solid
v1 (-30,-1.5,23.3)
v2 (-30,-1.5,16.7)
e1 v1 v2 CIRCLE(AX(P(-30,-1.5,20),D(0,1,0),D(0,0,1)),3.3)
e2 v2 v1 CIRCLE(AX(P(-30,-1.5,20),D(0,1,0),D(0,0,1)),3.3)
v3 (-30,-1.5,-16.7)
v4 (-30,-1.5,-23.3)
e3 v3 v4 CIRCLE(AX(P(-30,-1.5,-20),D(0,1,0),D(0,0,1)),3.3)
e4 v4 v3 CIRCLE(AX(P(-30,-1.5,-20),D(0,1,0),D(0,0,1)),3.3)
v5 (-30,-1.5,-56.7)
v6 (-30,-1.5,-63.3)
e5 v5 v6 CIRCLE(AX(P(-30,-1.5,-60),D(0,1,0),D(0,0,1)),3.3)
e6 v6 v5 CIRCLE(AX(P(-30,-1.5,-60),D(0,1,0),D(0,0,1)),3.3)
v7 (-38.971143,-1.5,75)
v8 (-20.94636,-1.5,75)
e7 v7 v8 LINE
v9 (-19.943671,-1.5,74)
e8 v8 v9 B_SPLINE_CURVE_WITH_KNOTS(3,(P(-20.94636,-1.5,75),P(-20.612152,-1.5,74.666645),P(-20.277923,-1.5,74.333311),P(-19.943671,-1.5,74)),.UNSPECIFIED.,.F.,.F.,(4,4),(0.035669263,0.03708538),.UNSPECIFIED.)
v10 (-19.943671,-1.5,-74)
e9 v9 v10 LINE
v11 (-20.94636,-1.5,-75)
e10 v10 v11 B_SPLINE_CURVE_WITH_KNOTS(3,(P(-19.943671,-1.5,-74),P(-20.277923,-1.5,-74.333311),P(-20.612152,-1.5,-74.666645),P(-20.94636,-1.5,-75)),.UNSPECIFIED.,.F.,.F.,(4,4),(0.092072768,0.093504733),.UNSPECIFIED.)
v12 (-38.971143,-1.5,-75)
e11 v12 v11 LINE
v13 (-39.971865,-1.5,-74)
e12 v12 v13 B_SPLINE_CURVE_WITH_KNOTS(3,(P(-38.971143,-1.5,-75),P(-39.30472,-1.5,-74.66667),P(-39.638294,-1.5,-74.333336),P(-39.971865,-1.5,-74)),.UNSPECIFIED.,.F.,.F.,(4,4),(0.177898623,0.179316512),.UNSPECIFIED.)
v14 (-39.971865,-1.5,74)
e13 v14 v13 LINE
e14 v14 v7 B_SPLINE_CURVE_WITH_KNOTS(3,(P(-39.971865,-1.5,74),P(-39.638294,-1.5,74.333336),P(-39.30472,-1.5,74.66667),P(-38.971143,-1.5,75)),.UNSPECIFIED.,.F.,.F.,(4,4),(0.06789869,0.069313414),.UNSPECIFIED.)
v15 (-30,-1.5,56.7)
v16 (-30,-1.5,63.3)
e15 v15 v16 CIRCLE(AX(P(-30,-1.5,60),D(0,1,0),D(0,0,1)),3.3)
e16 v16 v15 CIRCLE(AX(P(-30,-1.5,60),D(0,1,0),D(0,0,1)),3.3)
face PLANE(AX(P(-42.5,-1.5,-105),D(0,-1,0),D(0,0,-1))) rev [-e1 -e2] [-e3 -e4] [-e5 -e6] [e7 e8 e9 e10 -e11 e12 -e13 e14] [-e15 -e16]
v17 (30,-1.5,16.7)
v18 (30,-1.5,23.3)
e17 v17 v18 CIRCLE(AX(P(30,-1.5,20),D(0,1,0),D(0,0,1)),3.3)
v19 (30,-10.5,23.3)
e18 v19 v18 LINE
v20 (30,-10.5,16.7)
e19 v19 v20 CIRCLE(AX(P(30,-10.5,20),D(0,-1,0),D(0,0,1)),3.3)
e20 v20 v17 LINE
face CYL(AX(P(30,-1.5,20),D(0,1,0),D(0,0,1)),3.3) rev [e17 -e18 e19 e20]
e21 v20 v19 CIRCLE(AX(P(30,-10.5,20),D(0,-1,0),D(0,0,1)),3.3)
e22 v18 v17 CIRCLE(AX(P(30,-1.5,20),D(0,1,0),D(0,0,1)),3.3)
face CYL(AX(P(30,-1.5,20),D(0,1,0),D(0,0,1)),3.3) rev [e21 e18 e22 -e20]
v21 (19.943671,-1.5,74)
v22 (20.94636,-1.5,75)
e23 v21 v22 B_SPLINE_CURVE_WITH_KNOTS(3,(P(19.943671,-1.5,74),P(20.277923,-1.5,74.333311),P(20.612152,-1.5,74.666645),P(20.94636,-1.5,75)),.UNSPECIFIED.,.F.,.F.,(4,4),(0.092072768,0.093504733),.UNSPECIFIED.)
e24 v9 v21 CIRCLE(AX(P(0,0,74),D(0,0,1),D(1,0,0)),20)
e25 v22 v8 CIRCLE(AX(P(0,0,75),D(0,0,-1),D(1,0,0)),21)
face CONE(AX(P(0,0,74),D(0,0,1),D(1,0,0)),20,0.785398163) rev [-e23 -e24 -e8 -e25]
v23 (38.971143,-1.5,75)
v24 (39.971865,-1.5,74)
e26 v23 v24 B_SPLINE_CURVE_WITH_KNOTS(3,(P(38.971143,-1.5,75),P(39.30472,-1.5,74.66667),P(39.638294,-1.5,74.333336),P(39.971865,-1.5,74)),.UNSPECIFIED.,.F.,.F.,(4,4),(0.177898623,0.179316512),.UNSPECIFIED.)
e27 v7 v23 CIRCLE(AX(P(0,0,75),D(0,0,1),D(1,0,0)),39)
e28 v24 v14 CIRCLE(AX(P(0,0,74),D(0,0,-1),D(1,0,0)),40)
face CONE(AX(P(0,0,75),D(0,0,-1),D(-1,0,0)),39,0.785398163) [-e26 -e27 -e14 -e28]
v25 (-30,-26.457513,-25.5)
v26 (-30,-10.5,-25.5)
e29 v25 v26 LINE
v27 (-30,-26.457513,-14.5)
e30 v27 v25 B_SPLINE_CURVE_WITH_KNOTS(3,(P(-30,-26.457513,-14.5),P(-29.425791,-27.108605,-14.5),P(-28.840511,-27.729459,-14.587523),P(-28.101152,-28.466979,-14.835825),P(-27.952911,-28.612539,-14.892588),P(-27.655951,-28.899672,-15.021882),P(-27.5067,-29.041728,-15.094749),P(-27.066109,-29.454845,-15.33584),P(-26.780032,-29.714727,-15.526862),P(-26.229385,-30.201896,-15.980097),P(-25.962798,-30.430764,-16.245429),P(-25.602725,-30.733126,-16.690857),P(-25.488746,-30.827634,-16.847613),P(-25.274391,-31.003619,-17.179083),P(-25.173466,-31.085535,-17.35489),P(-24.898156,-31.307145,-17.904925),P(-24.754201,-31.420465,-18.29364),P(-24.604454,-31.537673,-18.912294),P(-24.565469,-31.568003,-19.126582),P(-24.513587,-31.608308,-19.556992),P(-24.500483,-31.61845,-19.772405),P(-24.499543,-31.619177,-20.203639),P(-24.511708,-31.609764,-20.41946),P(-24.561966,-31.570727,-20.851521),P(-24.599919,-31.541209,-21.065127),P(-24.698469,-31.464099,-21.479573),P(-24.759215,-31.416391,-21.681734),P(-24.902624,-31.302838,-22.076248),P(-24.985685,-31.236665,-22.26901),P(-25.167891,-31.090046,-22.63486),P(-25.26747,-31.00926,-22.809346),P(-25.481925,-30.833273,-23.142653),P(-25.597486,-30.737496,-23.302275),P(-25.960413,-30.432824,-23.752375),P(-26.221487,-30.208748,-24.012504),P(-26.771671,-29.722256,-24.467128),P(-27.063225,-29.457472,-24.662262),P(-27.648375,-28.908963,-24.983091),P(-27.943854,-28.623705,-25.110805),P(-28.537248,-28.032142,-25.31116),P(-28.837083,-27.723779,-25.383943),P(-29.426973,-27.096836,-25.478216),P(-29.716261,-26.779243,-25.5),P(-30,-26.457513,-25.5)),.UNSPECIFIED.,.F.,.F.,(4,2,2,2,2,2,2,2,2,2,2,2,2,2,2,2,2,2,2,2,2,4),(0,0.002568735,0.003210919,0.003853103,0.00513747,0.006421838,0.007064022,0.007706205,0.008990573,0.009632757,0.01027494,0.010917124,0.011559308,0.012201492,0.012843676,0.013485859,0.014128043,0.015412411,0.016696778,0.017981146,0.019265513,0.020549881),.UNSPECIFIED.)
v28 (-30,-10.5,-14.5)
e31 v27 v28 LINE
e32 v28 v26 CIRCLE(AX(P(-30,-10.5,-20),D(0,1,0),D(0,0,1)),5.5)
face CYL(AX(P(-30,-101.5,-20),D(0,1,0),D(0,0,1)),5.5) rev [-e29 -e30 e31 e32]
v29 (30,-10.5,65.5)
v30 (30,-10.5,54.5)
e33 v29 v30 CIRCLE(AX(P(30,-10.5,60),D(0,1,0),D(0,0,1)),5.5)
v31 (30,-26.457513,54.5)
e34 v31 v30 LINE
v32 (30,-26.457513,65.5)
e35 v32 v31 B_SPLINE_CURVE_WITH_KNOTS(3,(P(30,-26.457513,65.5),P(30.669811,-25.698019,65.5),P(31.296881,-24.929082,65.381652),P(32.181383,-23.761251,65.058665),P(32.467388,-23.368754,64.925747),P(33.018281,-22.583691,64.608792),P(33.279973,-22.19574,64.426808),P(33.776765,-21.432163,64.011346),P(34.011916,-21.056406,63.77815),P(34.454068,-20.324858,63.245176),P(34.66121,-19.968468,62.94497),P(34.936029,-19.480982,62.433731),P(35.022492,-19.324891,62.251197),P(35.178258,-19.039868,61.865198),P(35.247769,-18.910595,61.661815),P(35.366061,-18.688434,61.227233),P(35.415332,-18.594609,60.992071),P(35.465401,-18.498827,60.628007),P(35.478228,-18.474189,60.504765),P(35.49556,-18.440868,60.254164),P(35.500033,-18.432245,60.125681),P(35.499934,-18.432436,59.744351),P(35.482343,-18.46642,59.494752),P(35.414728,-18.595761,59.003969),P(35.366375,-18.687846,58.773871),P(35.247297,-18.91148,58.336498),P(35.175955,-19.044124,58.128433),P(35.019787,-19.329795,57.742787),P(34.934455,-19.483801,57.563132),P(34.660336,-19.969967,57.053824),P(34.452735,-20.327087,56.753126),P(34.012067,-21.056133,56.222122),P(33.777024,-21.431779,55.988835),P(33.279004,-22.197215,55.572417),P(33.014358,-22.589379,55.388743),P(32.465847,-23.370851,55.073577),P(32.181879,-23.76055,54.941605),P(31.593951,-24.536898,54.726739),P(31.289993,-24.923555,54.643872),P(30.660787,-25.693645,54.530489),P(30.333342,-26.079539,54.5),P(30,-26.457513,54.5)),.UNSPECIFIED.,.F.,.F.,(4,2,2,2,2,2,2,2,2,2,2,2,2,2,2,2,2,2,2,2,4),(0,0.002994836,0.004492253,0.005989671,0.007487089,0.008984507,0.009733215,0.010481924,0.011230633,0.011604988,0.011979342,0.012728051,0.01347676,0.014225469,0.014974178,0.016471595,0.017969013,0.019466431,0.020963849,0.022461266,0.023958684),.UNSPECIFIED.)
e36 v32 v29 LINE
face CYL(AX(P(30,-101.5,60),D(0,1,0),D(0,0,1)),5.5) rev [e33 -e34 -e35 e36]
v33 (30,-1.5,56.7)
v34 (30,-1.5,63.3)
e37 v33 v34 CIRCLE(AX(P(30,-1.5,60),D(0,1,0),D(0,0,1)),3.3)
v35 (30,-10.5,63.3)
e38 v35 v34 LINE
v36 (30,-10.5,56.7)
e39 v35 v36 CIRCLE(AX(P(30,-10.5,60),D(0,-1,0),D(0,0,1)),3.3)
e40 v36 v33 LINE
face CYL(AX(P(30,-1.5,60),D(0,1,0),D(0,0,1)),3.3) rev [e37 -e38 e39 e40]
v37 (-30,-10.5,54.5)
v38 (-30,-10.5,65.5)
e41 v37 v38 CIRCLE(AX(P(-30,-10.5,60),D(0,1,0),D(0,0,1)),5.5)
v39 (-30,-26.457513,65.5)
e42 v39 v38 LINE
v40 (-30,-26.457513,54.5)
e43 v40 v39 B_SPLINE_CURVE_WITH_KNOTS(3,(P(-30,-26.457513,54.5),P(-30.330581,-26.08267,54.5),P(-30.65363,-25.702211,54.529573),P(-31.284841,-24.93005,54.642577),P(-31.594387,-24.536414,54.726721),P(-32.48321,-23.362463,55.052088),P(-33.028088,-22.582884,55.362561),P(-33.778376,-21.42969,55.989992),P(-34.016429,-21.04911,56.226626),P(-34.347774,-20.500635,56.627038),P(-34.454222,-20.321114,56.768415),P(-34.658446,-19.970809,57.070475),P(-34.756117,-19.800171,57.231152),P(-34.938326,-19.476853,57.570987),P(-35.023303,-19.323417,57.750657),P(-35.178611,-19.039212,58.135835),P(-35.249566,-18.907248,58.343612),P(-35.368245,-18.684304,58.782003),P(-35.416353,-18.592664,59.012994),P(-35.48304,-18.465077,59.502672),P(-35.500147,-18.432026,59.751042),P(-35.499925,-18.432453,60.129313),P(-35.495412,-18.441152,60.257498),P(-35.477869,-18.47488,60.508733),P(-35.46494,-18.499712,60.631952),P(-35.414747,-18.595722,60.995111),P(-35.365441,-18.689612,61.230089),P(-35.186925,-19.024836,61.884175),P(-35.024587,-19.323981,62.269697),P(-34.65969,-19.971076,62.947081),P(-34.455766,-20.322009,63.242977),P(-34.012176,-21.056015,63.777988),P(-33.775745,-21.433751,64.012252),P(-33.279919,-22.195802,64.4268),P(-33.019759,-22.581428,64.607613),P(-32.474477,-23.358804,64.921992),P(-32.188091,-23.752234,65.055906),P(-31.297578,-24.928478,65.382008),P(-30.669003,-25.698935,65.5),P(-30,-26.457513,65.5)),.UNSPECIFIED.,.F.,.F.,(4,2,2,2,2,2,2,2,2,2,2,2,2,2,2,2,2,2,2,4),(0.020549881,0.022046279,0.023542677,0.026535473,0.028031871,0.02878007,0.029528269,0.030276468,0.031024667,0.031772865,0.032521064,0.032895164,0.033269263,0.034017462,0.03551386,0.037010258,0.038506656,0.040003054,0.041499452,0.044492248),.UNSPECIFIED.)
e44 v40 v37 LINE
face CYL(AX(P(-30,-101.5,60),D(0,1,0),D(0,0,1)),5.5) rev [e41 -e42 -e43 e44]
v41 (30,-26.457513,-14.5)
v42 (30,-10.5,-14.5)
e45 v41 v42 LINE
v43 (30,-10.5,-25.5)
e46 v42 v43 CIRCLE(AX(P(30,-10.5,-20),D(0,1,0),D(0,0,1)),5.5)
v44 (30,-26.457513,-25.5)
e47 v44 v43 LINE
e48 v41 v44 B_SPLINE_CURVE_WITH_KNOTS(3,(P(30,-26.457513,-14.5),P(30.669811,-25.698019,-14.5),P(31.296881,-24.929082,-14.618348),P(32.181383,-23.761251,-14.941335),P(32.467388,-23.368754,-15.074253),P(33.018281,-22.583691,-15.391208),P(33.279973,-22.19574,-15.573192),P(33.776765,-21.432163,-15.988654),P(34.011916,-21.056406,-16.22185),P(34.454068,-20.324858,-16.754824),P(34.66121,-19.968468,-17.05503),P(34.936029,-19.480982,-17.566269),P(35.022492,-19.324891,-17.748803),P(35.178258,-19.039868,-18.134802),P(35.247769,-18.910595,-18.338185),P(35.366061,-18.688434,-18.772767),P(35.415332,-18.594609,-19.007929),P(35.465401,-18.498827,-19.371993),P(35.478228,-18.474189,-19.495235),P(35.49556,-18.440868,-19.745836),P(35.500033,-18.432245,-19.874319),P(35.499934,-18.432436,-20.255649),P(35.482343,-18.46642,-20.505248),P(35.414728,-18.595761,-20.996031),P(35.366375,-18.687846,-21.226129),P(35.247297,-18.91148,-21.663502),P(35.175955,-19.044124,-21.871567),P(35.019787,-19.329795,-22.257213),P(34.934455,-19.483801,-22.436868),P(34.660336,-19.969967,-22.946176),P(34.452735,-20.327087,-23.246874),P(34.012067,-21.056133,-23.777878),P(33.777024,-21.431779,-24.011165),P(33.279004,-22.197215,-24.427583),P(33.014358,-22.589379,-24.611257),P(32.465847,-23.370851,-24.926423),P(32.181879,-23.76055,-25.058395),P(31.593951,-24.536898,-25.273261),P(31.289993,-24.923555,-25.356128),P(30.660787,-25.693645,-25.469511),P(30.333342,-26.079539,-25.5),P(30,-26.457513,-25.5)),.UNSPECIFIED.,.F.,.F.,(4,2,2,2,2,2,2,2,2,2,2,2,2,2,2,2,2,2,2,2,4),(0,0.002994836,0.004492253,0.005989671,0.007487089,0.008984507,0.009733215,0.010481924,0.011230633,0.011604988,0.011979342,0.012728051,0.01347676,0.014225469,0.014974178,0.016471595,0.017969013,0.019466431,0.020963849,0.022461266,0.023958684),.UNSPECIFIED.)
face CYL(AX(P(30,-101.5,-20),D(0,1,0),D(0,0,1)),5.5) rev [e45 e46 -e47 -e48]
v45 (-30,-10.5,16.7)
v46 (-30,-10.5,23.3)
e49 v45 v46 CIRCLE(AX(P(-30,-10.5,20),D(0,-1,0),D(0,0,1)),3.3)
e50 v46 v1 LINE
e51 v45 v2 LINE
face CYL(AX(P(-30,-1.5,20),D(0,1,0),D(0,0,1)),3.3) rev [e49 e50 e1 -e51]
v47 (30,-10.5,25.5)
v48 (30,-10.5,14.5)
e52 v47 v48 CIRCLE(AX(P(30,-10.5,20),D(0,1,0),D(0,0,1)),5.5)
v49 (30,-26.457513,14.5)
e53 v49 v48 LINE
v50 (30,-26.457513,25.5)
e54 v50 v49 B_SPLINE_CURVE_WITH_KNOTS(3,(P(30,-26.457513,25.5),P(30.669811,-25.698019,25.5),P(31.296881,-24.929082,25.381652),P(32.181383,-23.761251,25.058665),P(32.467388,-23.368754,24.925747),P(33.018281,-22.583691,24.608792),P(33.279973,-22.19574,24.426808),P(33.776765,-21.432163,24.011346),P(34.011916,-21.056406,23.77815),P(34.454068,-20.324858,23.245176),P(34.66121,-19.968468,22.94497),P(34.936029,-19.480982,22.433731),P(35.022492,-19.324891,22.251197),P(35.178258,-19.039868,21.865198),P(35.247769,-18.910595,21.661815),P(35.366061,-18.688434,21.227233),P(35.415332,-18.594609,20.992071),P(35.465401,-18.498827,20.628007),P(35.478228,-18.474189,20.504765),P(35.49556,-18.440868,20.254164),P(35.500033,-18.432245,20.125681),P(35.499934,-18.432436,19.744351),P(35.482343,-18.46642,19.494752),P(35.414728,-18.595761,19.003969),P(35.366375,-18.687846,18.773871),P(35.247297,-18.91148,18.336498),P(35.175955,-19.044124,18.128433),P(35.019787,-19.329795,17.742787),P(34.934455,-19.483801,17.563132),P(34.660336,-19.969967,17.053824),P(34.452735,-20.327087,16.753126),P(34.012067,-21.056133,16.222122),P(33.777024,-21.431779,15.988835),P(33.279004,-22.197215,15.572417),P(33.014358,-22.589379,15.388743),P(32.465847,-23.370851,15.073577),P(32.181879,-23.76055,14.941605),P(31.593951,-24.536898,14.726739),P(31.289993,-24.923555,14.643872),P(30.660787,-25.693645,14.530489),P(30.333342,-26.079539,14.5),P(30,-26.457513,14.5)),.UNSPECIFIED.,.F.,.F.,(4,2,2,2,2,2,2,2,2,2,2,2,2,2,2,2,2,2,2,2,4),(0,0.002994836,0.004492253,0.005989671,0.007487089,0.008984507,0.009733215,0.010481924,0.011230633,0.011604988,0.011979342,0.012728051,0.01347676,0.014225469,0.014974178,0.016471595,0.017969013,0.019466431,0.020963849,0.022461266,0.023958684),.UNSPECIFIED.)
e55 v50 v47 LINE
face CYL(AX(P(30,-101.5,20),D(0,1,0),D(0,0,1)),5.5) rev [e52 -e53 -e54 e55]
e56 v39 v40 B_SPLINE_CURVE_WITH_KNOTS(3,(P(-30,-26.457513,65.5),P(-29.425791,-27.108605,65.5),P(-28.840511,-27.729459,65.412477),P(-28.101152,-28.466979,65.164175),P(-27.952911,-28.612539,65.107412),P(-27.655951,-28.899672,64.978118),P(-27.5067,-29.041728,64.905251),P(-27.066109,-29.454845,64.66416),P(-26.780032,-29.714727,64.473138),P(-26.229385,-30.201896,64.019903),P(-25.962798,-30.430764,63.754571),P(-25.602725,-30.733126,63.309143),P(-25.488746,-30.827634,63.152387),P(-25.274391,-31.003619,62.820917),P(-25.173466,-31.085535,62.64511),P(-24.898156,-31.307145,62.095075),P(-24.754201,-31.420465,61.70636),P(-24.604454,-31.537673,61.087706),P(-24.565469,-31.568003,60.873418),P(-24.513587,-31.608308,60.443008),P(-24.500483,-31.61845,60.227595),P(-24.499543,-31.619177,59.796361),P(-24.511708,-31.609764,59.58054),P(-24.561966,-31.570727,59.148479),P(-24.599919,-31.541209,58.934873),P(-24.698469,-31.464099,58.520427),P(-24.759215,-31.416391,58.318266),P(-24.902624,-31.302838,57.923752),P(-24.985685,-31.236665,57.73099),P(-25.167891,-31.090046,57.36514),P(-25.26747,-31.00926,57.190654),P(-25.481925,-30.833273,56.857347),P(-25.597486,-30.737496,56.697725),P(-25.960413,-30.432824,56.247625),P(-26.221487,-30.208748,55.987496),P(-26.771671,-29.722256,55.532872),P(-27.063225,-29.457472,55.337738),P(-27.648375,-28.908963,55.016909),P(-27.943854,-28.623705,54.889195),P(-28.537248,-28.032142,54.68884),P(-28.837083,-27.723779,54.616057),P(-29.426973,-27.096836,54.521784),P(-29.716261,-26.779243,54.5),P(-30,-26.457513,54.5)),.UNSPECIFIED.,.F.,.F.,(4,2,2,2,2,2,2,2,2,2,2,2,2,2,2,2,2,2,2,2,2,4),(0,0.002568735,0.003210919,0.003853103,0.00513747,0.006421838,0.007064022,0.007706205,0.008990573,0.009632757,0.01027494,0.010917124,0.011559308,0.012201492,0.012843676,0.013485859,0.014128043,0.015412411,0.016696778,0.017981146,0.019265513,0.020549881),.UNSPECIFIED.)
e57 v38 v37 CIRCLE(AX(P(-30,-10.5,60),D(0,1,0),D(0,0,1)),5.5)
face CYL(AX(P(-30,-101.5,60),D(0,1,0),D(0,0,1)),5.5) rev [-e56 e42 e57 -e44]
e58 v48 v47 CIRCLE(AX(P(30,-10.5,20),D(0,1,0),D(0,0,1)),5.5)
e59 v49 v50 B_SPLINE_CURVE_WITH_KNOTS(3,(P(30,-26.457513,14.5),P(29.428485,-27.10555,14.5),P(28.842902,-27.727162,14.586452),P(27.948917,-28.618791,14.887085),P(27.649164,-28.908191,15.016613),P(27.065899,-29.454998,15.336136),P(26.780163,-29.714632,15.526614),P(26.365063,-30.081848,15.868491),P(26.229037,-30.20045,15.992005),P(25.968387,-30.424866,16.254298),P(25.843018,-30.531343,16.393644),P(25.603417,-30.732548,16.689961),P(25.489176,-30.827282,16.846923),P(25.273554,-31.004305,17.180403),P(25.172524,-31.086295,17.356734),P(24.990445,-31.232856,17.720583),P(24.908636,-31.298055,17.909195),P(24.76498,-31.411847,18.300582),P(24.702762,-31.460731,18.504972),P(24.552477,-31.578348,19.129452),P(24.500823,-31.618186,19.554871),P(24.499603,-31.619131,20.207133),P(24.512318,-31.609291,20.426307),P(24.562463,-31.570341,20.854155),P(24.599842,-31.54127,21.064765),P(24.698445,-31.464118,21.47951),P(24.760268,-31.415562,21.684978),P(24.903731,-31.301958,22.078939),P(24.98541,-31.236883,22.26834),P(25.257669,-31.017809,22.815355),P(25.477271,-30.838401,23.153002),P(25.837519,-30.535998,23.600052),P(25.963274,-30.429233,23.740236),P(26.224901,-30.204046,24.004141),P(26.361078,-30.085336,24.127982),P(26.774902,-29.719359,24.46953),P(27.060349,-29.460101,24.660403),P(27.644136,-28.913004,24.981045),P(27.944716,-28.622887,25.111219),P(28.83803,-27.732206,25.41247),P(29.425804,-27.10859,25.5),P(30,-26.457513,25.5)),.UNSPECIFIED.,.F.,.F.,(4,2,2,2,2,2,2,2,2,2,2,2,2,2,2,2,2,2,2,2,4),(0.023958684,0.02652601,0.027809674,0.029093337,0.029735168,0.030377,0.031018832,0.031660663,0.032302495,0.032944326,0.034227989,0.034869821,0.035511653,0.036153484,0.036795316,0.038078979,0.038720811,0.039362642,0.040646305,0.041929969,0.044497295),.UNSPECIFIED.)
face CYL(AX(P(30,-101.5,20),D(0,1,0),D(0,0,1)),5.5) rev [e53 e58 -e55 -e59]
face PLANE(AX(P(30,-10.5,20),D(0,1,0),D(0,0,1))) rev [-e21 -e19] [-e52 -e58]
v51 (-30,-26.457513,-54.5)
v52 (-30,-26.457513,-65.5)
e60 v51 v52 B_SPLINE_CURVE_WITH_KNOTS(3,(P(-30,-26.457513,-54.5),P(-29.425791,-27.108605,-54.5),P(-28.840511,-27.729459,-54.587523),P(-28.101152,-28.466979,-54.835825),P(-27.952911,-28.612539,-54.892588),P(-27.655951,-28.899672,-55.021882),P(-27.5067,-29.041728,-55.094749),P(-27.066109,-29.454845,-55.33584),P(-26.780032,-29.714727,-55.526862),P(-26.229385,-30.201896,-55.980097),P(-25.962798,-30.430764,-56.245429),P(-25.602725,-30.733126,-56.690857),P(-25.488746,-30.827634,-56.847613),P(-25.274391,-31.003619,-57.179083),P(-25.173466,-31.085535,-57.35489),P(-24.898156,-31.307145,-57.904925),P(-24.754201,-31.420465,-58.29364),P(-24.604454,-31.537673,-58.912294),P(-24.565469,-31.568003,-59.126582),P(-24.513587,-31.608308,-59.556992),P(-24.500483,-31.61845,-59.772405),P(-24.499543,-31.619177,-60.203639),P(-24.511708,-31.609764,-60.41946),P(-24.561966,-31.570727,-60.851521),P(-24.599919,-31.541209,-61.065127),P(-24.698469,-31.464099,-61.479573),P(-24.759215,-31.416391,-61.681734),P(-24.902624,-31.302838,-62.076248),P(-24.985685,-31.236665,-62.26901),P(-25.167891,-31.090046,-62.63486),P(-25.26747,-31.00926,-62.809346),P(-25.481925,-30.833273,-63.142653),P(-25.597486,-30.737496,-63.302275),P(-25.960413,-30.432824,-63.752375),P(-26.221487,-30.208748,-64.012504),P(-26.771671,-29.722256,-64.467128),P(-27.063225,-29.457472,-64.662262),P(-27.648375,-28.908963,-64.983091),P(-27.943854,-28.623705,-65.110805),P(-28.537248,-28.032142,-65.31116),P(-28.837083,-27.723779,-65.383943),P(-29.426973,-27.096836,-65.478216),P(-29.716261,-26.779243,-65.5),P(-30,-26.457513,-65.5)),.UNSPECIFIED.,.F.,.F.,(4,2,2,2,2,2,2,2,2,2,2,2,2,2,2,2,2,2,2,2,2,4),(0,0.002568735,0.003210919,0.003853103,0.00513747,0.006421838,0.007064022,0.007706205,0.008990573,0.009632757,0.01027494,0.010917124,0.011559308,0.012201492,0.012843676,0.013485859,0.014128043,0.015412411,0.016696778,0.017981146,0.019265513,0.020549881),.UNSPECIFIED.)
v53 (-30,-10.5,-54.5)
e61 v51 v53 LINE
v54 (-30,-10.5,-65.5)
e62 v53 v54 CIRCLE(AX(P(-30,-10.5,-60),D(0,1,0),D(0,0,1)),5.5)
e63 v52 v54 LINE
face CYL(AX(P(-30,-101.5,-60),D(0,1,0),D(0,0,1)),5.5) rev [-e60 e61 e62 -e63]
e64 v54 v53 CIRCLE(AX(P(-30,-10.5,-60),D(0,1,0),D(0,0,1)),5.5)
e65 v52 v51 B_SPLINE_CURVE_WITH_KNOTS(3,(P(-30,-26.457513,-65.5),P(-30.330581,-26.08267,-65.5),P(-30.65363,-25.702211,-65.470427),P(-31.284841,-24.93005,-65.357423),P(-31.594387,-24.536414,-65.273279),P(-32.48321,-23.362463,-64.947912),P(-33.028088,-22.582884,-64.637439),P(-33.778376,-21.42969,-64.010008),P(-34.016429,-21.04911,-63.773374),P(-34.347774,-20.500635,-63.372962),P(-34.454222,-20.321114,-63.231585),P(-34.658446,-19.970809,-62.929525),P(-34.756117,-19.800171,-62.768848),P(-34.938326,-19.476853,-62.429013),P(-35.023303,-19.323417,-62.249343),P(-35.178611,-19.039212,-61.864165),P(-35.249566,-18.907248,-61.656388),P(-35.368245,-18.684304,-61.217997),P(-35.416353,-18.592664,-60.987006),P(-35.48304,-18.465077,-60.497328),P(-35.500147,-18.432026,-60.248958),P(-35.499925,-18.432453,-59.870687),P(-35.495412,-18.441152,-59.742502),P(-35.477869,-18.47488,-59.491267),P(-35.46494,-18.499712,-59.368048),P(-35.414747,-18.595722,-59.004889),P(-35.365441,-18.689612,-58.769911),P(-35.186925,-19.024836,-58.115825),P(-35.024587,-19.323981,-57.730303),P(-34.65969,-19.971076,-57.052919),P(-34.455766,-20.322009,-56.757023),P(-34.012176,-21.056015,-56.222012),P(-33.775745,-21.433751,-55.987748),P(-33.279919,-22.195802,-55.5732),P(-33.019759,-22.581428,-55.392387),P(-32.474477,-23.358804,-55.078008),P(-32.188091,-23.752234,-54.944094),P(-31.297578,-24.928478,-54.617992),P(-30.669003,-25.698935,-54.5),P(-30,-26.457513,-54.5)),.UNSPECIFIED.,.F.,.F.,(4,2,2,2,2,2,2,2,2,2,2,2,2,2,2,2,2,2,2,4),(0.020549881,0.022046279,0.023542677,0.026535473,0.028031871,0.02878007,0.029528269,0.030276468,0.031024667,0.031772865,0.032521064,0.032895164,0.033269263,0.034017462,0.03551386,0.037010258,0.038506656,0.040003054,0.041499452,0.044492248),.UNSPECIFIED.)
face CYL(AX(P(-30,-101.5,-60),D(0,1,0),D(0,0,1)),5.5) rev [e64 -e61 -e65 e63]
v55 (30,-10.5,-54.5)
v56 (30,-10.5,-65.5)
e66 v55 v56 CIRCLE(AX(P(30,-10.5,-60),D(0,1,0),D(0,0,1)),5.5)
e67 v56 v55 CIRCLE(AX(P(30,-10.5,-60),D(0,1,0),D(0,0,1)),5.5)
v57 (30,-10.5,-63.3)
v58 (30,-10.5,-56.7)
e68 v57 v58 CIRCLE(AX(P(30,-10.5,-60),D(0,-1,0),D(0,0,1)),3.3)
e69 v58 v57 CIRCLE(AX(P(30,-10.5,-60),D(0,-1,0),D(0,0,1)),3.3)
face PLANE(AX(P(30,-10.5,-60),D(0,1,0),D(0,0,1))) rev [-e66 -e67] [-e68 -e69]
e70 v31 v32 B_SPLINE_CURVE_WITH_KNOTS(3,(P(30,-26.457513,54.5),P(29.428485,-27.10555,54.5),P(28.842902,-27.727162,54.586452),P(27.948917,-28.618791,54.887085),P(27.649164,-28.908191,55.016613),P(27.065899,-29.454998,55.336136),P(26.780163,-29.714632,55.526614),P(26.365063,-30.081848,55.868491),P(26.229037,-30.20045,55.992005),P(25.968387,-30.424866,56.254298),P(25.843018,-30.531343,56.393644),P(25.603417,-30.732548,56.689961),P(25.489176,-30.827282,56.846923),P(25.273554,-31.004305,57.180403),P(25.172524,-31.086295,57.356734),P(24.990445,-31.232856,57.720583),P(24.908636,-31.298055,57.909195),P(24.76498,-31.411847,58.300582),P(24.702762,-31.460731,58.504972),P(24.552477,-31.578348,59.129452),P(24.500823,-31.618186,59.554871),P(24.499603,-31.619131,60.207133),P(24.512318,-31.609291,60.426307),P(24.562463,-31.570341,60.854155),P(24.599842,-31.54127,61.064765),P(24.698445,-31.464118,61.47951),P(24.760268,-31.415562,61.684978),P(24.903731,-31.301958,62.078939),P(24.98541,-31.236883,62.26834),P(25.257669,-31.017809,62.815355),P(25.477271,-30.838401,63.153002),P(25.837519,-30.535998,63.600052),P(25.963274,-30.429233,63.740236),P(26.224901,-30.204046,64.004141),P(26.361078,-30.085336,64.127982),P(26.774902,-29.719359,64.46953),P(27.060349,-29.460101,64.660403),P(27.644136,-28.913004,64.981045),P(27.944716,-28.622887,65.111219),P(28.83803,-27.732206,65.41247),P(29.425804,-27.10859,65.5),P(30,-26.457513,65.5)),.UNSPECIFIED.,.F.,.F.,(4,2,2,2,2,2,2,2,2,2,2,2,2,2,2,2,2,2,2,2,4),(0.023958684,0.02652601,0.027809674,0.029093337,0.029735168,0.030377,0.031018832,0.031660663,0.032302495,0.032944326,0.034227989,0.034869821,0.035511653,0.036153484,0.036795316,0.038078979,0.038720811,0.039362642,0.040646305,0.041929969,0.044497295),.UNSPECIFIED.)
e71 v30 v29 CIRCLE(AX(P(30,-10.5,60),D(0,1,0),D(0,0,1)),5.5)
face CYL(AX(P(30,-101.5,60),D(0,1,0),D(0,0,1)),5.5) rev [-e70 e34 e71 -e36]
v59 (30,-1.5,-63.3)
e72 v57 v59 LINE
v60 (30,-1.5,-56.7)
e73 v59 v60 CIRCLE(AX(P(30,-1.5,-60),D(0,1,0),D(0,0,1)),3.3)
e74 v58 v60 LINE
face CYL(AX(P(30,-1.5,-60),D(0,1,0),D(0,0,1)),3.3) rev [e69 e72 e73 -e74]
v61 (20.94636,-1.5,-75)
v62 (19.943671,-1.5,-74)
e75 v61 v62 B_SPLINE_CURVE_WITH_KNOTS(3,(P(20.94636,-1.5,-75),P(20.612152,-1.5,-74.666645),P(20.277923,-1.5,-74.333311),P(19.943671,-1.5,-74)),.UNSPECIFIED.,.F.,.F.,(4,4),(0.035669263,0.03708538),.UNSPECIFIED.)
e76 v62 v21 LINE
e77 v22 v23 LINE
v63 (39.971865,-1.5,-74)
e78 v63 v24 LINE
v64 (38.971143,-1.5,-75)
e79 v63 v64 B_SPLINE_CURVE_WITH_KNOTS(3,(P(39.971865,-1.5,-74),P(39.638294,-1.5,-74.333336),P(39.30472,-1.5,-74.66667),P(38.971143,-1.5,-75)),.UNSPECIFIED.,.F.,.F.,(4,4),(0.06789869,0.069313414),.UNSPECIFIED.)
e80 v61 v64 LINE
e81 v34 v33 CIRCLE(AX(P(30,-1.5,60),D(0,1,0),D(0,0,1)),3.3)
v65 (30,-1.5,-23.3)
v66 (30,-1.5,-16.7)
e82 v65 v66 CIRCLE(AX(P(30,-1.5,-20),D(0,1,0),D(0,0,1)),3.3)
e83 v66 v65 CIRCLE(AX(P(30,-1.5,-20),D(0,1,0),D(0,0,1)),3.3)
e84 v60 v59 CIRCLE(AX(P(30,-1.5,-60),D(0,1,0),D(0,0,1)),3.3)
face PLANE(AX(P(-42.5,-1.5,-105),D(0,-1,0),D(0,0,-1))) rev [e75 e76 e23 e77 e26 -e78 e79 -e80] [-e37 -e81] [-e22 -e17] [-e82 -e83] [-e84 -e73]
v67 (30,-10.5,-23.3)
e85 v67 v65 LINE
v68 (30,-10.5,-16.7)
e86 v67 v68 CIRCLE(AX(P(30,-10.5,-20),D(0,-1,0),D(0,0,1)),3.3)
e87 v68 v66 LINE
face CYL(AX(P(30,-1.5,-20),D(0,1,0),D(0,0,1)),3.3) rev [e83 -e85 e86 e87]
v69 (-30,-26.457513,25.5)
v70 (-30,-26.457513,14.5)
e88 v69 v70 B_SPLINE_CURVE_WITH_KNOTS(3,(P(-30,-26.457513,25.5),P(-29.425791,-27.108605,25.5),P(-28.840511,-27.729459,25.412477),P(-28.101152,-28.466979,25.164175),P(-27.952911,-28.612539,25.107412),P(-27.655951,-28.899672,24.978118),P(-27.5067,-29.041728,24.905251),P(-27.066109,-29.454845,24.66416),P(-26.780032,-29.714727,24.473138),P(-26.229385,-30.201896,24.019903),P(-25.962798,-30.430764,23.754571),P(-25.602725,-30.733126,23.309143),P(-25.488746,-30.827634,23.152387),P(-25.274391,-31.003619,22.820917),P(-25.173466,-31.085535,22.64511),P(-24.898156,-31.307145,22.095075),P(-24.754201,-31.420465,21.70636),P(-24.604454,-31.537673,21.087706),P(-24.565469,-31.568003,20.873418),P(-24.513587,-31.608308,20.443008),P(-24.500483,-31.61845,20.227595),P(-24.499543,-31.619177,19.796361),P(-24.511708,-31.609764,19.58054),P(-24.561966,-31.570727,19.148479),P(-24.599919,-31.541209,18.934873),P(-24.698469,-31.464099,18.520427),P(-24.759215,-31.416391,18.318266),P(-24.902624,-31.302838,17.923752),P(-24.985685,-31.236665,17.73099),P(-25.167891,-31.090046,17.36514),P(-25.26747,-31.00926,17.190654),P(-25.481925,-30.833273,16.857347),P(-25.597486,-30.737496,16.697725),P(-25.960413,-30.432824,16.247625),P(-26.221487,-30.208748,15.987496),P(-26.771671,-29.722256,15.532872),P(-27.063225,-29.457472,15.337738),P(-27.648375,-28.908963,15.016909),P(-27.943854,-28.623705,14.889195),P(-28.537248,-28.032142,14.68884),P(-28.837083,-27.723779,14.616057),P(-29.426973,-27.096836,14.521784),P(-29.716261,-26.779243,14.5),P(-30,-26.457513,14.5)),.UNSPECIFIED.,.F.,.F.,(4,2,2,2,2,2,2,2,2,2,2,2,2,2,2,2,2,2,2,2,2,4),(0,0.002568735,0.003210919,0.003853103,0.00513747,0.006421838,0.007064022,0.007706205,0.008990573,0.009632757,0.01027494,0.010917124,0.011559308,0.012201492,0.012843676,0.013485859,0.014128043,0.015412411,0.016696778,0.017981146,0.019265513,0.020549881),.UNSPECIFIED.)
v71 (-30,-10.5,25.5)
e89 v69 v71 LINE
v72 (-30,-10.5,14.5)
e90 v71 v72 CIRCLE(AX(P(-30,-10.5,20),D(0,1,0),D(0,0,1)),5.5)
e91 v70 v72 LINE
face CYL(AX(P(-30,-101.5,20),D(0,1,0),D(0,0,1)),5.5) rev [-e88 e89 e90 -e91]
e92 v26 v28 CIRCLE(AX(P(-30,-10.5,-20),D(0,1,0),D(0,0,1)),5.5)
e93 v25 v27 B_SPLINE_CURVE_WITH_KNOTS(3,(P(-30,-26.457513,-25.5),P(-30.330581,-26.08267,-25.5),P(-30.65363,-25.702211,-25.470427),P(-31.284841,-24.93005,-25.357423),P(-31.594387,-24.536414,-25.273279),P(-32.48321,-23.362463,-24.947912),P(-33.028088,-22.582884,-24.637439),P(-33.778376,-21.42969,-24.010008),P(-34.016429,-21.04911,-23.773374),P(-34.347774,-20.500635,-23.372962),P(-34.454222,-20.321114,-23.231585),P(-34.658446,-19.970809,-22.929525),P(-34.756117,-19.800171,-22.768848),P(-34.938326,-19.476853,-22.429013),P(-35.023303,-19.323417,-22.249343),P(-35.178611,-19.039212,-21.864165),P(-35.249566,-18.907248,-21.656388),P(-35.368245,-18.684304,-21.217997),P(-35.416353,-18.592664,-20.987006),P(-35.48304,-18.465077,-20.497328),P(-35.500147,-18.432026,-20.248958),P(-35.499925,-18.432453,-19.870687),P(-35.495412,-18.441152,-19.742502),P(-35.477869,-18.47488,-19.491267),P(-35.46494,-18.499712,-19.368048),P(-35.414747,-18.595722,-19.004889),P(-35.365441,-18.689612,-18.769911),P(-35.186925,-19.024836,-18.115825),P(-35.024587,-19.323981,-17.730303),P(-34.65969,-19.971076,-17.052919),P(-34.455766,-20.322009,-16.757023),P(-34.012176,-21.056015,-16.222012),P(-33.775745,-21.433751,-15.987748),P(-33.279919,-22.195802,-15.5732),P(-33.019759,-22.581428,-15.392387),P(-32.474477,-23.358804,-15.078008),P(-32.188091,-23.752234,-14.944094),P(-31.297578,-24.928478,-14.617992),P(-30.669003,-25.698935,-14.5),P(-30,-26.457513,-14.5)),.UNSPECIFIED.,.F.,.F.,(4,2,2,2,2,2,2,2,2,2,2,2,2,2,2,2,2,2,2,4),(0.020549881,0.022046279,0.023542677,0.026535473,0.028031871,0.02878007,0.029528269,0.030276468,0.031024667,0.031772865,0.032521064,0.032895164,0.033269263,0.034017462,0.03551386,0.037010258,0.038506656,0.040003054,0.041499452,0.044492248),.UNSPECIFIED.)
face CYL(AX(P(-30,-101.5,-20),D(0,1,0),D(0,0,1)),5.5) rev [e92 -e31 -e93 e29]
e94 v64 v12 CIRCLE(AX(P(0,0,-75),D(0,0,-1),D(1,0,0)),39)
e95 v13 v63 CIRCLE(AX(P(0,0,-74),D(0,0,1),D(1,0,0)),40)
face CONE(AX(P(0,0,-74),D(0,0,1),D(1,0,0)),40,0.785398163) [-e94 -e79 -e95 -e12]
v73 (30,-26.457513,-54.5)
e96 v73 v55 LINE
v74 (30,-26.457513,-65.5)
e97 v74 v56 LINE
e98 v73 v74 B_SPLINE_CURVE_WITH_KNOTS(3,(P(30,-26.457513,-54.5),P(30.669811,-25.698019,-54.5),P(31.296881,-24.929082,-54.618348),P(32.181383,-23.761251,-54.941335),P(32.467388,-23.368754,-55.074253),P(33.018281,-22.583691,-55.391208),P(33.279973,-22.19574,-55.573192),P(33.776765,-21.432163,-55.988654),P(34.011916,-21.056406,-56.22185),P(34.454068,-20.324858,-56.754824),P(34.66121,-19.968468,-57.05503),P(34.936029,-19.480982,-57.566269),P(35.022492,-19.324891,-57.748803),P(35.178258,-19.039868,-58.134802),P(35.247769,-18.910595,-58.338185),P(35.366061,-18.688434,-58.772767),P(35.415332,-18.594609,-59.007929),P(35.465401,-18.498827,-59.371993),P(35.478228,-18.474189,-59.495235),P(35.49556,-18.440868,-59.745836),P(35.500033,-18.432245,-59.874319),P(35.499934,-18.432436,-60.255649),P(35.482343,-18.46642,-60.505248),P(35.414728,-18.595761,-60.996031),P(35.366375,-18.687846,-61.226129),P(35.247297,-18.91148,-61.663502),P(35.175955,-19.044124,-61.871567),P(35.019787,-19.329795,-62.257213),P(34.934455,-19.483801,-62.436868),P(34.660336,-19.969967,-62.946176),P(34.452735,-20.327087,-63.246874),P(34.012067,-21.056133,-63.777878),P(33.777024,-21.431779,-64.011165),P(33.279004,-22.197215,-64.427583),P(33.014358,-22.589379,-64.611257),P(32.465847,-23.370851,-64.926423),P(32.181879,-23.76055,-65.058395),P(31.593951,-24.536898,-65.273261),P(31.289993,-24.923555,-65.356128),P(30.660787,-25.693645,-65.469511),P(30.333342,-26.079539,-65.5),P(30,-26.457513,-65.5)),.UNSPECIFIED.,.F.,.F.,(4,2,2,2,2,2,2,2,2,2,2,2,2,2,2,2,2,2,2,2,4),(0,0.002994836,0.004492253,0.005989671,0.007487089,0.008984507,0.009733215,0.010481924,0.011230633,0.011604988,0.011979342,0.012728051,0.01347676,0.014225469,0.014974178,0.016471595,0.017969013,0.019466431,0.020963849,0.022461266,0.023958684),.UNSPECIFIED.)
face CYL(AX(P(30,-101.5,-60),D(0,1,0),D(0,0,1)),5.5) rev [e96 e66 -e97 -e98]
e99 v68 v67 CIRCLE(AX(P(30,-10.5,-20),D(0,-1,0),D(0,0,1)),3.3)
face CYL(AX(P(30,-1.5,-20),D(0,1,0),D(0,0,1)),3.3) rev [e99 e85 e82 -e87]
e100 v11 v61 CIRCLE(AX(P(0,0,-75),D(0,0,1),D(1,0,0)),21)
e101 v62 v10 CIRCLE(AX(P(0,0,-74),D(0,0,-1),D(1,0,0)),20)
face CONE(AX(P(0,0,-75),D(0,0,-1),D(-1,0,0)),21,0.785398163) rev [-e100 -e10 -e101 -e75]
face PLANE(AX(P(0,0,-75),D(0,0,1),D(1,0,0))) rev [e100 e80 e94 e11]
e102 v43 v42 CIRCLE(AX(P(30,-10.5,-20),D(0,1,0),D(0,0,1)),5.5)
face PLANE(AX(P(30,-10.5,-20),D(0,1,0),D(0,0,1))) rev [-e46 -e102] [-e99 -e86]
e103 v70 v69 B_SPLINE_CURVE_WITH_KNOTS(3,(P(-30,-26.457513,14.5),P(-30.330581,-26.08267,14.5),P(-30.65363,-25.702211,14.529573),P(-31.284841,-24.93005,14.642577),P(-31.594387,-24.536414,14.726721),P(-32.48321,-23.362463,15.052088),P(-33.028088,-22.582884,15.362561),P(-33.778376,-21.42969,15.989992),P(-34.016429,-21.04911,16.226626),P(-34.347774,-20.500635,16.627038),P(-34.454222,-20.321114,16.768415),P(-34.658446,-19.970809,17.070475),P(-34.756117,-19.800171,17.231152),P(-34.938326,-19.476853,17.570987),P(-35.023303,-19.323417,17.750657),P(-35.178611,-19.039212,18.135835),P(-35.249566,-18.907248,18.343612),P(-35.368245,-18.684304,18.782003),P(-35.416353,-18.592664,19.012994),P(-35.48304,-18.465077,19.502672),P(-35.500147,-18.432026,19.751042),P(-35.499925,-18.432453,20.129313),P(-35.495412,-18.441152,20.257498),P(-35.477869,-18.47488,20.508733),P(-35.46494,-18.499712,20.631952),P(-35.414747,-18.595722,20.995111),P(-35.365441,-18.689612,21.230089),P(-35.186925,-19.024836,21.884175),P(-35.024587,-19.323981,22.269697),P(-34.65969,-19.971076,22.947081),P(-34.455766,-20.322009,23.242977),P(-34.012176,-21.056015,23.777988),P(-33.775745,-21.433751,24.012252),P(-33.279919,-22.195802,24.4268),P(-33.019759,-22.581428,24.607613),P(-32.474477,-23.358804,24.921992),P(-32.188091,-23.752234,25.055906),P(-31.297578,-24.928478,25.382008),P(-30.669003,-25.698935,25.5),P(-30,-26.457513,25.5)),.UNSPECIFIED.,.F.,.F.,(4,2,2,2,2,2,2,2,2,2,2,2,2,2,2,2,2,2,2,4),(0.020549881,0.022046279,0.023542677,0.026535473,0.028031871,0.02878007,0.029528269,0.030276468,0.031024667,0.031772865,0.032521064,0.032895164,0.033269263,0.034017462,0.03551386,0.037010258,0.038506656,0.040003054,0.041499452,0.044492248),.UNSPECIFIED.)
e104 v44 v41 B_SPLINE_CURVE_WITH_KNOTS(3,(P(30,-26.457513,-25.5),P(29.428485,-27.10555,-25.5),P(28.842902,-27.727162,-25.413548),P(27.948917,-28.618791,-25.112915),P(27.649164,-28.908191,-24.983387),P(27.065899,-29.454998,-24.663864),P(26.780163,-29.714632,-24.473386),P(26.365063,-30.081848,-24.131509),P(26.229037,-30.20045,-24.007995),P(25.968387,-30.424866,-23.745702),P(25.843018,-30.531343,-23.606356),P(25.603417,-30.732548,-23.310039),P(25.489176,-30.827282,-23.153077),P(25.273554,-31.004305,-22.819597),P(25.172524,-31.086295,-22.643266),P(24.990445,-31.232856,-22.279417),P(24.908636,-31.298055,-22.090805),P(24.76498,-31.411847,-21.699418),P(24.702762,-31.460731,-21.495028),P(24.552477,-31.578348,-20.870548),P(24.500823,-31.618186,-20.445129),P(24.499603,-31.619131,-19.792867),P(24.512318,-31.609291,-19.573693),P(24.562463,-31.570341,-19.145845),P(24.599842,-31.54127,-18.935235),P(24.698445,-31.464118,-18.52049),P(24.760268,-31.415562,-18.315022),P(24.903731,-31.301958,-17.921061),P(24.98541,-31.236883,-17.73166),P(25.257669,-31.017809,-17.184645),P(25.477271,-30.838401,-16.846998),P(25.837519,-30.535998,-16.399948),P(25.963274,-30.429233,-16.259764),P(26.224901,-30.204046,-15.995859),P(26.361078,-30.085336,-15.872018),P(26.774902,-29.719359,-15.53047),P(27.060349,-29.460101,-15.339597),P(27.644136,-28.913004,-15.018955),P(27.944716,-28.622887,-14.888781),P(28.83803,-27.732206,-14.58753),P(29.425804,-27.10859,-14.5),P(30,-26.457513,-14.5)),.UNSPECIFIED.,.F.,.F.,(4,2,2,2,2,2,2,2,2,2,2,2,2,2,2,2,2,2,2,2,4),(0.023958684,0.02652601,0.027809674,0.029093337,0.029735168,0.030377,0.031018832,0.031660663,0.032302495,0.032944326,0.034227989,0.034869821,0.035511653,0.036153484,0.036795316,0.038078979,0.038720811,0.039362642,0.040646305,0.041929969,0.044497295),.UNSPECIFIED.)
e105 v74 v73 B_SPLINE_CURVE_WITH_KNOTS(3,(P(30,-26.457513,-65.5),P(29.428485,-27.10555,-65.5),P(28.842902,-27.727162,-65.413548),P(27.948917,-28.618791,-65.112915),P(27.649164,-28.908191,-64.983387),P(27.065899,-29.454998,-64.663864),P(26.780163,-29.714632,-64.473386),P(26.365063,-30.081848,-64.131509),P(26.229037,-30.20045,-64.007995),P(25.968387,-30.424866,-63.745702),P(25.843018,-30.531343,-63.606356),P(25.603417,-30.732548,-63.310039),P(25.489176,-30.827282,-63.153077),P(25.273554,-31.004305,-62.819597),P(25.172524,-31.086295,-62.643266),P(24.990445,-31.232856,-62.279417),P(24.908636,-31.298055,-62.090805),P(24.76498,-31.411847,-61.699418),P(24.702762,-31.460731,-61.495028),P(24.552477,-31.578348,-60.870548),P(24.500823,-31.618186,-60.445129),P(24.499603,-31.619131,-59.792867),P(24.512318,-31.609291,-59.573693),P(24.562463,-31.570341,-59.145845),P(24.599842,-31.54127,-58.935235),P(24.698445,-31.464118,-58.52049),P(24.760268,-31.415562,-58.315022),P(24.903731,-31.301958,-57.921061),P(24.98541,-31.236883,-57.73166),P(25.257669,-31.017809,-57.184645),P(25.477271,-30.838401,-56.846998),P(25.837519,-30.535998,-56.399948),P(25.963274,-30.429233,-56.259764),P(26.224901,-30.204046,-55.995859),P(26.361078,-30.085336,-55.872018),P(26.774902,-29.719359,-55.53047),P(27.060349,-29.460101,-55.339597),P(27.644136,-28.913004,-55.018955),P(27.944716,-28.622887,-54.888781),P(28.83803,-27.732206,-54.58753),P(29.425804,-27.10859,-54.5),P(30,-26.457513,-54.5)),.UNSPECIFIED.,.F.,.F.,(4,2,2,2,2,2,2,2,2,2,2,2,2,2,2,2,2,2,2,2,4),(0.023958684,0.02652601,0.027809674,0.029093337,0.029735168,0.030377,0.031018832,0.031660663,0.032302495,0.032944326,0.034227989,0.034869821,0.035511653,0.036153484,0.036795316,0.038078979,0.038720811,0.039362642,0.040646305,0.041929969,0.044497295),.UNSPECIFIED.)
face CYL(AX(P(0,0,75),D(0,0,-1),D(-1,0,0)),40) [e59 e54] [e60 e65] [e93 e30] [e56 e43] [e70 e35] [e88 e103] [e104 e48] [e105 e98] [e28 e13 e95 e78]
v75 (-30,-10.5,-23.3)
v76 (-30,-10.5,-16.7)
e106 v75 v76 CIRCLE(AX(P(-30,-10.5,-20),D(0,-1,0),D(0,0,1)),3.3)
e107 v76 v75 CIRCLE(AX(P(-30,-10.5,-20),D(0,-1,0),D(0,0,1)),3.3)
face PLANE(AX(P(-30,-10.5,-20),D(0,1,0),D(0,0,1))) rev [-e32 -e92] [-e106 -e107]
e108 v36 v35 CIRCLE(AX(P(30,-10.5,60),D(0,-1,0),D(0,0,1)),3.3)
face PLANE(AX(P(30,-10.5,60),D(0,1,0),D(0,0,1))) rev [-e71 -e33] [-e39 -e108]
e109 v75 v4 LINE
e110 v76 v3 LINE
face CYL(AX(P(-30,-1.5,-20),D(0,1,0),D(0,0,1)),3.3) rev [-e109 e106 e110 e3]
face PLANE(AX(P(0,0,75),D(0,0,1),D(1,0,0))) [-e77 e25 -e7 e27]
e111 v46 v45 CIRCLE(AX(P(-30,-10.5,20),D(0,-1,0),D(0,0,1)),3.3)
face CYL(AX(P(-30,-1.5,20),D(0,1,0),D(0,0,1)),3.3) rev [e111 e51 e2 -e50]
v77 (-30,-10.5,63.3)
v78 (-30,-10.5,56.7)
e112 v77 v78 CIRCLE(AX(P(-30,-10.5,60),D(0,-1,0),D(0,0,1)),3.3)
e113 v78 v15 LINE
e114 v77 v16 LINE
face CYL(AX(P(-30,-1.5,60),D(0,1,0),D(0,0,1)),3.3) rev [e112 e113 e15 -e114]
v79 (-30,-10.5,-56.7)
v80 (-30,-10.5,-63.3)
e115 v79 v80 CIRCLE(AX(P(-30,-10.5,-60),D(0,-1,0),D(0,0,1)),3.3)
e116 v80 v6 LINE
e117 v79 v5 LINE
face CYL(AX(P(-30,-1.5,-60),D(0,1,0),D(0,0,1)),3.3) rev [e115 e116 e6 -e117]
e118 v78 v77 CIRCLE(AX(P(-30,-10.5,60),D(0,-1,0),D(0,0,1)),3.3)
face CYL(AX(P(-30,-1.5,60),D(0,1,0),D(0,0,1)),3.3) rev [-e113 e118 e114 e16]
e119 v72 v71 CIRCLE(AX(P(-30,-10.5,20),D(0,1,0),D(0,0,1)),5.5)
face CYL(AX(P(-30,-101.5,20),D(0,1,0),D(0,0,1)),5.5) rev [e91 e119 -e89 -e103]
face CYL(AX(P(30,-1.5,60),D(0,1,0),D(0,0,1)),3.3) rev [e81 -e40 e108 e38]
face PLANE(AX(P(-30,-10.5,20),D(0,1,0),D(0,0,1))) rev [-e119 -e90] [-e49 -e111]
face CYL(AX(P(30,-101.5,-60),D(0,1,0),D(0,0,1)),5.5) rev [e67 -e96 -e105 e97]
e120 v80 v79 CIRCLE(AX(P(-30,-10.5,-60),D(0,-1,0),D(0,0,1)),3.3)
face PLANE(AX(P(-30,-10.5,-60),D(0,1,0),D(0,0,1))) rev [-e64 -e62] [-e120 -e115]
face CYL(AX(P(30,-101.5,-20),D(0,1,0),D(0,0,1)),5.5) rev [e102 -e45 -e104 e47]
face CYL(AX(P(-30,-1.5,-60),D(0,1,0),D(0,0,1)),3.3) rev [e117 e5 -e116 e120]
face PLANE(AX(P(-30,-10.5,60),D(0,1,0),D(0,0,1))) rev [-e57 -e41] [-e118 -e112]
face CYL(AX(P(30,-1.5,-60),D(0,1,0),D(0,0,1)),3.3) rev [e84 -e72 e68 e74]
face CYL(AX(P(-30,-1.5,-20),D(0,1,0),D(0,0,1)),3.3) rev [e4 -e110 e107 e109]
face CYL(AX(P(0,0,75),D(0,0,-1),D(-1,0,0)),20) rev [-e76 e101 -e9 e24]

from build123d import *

# Parameters (mm, degrees)
SKETCH1_R            = 40
BOSS_EXTRUDE1_DEPTH  = 75
CHAMFER1_SIZE        = 1
SKETCH2_W            = 85
SKETCH2_H            = 3
CUT_EXTRUDE1_DEPTH   = 180
CUT_EXTRUDE2_START   = -9
SKETCH6_R            = 5.5
CUT_EXTRUDE2_DEPTH   = 91
LPATTERN1_COUNT      = 4
LPATTERN1_PITCH      = 40
LPATTERN1_COUNT_DIR2 = 2
LPATTERN1_PITCH_DIR2 = 60


with BuildPart() as part:
    # Sketch1 → Boss-Extrude1 (new, symmetric)
    with BuildSketch(Plane.XY):
        Circle(SKETCH1_R)
        with BuildLine():
            Line((-4, 15.3), (4, 15.3))
            Line((4, 15.3), (4, 19.595917942))
            ThreePointArc((4, 19.595917942), (0, -20), (-4, 19.595917942))
            Line((-4, 19.595917942), (-4, 15.3))
        make_face(mode=Mode.SUBTRACT)
    extrude(amount=BOSS_EXTRUDE1_DEPTH, both=True)

    # Chamfer1
    chamfer1_edges = [part.edges().sort_by_distance(p)[0] for p in [
        (-40, 0, -75),
        (-40, 0, 75),
        (0, -20, -75),
        (0, -20, 75),
    ]]
    chamfer(chamfer1_edges, length=CHAMFER1_SIZE)

    # Sketch2 → Cut-Extrude1 (cut)
    with BuildSketch(Plane.XY.offset(75)):
        Rectangle(SKETCH2_W, SKETCH2_H)
    extrude(amount=-CUT_EXTRUDE1_DEPTH, mode=Mode.SUBTRACT)


with BuildPart() as cut_extrude1_kept_piece:
    # of the separate pieces the step leaves, the one the design keeps (cut_extrude1_pieces_kept)
    add(part.part.solids().sort_by_distance((-39.971865105, -1.5, -74))[0])

    # Sketch5 → M6 Clearance Hole1 (revolve, cut)
    with BuildSketch(Plane(origin=(30, -1.5, 60), x_dir=(0, 0, 1), z_dir=(1, 0, 0))):
        Polygon((0, 0), (0, 36.982840043), (3.3, 35), (3.3, 0), align=None)
    m6_clearance_hole1 = revolve(axis=Axis((30, 4.85, 60), (0, -1, 0)), mode=Mode.SUBTRACT)

    # Sketch6 → Cut-Extrude2 (cut)
    with BuildSketch(Plane(origin=(0, -1.5, 0), x_dir=(1, 0, 0), z_dir=(0, 1, 0)).offset(CUT_EXTRUDE2_START)):
        with Locations(Location((30, -60, 0), (0, 0, 270))):
            Circle(SKETCH6_R)
    cut_extrude2 = extrude(amount=-CUT_EXTRUDE2_DEPTH, mode=Mode.SUBTRACT)

    # LPattern1: M6 Clearance Hole1, Cut-Extrude2 4 × 2
    with Locations(*[(-j * LPATTERN1_PITCH_DIR2, 0, -i * LPATTERN1_PITCH) for i in range(LPATTERN1_COUNT) for j in range(LPATTERN1_COUNT_DIR2) if (i, j) != (0, 0)]):
        add(m6_clearance_hole1, mode=Mode.SUBTRACT)
        add(cut_extrude2, mode=Mode.SUBTRACT)


solid = cut_extrude1_kept_piece.part
